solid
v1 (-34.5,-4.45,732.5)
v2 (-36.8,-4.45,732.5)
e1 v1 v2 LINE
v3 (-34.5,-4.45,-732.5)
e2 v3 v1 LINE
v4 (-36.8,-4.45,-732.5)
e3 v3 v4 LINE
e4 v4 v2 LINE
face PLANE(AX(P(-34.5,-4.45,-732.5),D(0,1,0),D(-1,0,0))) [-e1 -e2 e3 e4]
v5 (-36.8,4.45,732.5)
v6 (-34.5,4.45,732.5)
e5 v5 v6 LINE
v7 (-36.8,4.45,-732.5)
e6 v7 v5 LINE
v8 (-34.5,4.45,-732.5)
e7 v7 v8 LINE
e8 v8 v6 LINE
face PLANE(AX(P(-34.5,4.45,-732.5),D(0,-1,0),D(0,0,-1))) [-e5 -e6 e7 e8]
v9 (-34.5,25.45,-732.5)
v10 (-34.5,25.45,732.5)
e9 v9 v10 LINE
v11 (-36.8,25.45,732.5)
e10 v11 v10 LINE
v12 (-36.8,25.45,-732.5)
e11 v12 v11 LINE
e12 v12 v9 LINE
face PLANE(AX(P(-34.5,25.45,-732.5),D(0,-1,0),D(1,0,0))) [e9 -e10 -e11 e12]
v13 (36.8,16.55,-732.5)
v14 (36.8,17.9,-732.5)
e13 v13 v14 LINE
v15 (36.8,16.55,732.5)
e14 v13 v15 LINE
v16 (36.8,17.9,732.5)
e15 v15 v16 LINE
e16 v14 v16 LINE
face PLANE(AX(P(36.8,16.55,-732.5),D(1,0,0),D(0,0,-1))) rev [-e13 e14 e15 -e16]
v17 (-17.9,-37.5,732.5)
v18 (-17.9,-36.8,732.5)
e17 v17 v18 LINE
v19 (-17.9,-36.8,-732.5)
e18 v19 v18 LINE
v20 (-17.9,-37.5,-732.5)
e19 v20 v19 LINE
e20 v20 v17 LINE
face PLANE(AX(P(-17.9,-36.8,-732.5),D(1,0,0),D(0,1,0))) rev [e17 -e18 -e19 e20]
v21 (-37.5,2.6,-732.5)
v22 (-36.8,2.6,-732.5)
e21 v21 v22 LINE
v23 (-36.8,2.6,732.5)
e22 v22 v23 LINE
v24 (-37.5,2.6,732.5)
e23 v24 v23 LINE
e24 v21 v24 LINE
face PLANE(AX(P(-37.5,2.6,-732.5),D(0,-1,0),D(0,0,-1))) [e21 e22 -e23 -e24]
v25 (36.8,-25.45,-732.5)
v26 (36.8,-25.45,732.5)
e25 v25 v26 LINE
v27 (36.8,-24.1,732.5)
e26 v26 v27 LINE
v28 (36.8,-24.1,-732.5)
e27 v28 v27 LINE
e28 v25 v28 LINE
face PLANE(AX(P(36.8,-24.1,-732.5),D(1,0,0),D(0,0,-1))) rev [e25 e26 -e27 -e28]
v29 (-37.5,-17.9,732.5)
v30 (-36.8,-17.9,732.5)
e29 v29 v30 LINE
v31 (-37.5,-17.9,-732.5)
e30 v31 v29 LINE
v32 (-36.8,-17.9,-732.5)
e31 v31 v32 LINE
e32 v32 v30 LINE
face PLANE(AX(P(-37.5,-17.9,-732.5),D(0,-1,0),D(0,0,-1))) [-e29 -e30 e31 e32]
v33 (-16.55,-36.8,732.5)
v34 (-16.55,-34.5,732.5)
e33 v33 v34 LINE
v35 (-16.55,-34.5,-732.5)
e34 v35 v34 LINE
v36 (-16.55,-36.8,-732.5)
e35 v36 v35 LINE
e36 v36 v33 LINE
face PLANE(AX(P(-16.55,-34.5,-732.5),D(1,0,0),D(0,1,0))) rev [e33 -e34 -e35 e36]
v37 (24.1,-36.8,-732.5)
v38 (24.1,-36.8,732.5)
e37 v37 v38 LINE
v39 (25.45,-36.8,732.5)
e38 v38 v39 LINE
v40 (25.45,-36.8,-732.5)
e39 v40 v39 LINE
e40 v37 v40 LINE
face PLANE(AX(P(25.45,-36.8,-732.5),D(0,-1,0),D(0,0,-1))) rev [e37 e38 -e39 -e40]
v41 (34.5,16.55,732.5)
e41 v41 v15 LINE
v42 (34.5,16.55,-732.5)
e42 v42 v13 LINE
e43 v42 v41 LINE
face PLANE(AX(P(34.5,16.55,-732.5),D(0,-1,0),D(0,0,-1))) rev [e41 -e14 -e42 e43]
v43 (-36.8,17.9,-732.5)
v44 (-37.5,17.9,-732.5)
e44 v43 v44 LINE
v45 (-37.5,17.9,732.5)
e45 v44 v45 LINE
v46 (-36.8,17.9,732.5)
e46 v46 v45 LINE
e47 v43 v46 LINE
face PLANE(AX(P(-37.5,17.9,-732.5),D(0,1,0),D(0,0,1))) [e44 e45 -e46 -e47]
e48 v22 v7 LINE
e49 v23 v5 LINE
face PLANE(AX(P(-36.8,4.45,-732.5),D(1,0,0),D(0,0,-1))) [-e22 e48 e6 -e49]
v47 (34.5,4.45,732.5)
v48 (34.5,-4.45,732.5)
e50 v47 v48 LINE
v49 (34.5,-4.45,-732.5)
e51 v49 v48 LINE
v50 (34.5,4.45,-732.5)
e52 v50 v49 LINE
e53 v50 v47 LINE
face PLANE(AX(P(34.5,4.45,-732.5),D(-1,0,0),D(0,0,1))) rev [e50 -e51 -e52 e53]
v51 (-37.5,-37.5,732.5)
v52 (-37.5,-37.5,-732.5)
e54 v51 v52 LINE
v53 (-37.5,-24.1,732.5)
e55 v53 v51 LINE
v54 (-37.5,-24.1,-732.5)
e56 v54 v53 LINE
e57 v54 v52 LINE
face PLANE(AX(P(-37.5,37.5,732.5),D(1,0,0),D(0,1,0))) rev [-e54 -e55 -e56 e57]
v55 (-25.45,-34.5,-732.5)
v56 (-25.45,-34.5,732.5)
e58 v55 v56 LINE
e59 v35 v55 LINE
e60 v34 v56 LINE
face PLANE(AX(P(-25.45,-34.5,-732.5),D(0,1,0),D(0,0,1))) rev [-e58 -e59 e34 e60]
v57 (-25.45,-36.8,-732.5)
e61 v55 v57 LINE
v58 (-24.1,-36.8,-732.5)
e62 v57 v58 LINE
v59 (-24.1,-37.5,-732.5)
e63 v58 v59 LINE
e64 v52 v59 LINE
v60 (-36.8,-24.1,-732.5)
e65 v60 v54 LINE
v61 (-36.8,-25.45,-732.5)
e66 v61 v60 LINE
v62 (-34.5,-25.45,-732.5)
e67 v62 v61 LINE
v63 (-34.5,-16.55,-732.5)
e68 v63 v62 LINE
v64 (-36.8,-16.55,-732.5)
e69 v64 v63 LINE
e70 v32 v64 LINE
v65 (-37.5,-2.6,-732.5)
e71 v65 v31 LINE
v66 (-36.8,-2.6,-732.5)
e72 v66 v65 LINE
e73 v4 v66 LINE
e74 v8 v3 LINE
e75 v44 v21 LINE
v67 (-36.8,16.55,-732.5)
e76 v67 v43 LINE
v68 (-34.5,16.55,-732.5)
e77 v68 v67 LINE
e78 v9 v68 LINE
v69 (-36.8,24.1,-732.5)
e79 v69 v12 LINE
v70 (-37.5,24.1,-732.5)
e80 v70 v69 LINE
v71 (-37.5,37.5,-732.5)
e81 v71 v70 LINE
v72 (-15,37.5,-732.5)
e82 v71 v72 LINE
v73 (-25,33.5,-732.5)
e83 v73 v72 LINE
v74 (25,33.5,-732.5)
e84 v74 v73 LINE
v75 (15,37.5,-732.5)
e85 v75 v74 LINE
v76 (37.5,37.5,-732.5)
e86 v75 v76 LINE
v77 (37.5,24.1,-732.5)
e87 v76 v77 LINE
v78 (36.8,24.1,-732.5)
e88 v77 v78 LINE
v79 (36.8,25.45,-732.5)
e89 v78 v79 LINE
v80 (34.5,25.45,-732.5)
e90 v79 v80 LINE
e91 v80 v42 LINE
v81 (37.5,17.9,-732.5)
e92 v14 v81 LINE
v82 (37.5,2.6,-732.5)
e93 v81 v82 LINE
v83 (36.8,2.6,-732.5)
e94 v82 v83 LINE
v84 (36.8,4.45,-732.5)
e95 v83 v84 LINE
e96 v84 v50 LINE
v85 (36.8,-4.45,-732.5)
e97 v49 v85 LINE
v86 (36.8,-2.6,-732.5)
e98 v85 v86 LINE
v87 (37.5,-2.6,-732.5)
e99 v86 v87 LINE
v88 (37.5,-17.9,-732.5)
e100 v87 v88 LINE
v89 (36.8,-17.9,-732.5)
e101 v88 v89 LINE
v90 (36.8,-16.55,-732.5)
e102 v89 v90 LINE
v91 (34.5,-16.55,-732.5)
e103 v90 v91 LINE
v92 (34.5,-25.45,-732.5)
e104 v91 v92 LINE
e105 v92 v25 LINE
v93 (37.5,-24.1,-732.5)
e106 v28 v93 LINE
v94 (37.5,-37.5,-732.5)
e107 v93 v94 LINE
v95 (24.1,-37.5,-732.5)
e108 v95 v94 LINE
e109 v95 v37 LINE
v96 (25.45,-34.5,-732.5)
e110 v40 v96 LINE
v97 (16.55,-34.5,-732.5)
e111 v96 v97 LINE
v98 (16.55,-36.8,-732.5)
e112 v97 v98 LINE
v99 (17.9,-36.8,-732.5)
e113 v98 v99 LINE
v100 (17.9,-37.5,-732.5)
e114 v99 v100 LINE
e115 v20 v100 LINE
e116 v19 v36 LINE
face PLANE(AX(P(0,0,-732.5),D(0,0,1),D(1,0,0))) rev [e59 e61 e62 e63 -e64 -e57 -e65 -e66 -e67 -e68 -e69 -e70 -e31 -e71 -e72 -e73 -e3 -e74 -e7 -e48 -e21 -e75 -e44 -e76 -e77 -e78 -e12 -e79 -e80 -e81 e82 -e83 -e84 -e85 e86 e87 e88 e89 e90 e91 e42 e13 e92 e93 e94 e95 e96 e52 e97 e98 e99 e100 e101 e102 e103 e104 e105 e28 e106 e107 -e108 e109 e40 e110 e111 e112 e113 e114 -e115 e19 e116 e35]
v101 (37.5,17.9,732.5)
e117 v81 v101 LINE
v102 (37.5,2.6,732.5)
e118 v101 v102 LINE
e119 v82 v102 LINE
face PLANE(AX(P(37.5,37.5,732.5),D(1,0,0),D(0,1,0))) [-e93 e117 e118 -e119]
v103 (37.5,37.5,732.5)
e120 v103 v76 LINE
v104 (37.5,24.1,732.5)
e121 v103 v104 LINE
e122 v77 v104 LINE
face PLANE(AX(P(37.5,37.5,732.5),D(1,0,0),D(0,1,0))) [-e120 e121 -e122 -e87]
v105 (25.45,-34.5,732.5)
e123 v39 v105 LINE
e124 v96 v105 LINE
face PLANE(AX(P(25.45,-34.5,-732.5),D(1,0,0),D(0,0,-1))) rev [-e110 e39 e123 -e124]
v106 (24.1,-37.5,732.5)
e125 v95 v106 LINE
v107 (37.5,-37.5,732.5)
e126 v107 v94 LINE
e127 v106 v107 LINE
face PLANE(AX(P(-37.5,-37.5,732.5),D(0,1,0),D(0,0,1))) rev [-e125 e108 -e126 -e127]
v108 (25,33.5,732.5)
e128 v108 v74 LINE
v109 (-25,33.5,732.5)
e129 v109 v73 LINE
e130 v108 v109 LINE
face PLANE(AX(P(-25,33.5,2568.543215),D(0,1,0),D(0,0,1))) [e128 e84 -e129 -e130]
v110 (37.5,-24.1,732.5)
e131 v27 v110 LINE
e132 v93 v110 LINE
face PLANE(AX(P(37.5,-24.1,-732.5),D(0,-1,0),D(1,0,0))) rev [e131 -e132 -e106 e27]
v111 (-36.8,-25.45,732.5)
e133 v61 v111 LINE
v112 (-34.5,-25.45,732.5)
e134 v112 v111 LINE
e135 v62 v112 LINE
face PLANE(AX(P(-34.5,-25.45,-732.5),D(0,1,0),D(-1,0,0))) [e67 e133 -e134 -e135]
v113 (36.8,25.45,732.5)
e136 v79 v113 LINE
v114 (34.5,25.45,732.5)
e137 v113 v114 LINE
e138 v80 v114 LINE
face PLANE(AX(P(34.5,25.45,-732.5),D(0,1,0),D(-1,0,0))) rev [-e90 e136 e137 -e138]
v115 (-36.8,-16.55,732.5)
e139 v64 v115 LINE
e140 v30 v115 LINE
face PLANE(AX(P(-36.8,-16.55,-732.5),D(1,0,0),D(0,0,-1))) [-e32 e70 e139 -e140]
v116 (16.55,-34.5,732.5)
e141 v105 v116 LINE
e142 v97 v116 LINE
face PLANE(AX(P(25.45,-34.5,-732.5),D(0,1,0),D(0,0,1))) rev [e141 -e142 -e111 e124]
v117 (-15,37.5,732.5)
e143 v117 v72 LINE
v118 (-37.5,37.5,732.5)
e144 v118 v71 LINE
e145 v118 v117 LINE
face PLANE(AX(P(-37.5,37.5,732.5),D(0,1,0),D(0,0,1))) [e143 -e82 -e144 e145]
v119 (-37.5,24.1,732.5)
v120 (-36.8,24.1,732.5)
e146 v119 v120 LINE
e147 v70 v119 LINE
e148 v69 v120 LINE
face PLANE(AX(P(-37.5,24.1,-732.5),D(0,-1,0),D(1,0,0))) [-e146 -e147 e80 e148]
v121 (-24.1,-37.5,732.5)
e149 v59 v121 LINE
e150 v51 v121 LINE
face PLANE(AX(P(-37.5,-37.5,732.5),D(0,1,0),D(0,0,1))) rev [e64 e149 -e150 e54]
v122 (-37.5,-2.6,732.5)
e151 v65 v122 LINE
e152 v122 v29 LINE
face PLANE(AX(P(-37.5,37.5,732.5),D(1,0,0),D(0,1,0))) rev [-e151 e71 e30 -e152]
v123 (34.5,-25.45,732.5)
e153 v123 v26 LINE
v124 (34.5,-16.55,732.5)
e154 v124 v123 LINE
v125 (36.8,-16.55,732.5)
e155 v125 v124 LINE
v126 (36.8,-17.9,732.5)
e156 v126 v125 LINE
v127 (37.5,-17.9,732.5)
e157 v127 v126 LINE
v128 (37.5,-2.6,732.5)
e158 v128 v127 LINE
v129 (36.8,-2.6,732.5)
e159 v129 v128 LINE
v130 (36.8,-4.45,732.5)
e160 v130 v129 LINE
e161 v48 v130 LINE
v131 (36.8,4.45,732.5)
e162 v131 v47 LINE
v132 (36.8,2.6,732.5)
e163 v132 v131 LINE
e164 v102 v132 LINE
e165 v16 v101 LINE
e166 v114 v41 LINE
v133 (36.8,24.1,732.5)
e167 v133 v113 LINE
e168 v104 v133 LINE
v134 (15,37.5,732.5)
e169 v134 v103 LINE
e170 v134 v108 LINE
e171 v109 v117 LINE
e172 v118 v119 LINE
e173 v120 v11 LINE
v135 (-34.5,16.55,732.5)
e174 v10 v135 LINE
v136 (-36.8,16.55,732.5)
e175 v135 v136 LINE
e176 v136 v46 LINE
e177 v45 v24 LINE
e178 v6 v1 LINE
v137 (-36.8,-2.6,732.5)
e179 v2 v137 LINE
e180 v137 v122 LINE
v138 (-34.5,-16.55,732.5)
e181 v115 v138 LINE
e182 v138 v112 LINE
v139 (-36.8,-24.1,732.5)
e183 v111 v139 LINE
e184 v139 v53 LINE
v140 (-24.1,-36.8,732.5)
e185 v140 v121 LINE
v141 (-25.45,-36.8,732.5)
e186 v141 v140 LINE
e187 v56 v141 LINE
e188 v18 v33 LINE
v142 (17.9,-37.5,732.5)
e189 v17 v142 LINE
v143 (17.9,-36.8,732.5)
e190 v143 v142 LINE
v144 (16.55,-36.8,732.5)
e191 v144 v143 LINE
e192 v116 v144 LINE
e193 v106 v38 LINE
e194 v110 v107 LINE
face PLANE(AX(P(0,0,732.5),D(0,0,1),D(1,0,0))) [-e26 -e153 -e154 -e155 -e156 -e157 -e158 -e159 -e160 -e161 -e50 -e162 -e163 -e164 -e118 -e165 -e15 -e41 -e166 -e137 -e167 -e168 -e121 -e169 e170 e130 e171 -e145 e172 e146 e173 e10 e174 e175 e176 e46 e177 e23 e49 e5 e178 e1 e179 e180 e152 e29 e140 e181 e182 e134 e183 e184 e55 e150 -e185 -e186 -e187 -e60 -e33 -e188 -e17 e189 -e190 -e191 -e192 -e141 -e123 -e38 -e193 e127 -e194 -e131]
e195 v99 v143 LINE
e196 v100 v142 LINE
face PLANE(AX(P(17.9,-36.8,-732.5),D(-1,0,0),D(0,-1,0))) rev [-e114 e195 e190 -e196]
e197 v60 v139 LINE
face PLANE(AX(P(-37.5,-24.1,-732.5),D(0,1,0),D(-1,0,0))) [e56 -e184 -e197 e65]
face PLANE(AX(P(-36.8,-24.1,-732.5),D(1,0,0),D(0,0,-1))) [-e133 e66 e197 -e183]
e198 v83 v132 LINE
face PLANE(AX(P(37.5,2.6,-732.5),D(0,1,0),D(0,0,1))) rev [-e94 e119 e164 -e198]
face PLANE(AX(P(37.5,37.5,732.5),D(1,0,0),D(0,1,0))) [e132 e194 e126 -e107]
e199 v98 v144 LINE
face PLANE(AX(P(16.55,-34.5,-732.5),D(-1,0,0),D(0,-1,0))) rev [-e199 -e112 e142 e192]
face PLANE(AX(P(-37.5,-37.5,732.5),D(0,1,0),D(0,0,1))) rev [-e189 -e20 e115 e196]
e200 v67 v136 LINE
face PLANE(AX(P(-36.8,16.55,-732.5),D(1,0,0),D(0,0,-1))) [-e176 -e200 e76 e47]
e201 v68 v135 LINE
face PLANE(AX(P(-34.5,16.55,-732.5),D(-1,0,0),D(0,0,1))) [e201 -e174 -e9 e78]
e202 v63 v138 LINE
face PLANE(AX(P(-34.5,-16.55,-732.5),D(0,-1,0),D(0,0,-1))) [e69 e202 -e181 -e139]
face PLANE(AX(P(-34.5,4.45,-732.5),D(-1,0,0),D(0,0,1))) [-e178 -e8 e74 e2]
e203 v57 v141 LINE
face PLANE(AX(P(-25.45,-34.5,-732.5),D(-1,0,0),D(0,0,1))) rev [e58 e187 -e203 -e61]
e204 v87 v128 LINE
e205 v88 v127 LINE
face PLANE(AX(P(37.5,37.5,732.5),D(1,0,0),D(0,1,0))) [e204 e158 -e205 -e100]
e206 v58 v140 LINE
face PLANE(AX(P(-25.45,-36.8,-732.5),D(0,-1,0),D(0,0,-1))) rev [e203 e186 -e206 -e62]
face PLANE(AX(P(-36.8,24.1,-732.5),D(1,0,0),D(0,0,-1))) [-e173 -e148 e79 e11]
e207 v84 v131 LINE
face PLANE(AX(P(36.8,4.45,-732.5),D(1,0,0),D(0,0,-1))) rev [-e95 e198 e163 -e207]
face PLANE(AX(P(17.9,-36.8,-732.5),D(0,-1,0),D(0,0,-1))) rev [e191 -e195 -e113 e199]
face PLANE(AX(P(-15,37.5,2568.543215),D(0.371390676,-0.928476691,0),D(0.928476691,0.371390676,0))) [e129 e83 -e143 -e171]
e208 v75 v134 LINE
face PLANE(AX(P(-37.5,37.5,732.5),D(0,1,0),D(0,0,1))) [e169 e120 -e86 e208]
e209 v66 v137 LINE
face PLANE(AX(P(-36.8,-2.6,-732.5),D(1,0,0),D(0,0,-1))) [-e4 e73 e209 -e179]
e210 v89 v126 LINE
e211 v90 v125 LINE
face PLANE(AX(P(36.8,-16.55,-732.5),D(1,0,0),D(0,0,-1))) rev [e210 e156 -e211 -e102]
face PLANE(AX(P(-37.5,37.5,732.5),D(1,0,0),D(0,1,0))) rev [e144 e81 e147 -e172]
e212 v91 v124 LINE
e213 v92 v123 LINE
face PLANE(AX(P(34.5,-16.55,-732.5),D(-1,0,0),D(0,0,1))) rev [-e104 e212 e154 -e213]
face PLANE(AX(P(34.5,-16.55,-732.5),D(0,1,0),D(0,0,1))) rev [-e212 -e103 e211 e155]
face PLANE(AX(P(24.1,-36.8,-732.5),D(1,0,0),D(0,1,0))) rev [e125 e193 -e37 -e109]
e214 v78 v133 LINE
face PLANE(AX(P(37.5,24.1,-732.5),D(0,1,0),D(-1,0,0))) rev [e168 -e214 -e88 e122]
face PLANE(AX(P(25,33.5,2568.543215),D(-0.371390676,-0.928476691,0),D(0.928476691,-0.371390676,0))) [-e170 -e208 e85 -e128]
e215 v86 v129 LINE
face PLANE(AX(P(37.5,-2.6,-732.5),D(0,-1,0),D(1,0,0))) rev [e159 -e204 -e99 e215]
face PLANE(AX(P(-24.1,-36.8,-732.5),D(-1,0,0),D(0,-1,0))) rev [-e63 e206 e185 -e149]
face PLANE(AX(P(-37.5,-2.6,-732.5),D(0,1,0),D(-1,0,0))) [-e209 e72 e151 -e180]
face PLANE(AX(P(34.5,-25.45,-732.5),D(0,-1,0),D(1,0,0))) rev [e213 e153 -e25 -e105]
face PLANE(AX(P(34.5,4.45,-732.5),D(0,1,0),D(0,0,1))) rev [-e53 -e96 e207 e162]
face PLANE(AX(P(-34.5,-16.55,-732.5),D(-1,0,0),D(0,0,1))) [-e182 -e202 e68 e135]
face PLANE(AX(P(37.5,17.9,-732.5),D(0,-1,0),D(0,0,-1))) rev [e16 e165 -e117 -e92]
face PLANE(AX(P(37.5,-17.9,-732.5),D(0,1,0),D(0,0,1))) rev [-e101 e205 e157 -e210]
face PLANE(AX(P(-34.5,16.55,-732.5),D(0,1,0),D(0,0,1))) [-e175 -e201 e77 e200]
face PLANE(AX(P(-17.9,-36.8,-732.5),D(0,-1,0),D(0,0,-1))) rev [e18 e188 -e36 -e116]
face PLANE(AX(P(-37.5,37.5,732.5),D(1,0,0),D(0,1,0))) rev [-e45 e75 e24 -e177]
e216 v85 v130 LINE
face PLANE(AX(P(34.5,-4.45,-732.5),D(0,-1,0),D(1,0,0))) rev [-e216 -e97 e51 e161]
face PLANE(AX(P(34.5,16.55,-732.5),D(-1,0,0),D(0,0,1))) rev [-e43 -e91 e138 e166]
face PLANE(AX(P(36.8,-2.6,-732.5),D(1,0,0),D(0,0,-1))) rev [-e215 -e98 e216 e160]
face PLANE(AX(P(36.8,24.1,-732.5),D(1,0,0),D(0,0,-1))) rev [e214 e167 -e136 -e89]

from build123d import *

# Parameters (mm, degrees)
SKETCH_1_W               = 75
SKETCH_1_H               = 75
EXTRUDE_1_DEPTH          = 732.5
CUT_EXTRUDE_1_DEPTH      = 732.5
CUT_EXTRUDE_2_DEPTH      = 1465
CUT_EXTRUDE_3_DEPTH      = 1466.959583345
CUT_EXTRUDE_3_DEPTH_BACK = 1466.959583345


with BuildPart() as part:
    # 草图1 → 凸台-拉伸1 (new, symmetric)
    with BuildSketch(Plane.XY):
        Rectangle(SKETCH_1_W, SKETCH_1_H)
    extrude(amount=EXTRUDE_1_DEPTH, both=True)

    # 草图2 → 切除-拉伸1 (cut, symmetric)
    with BuildSketch(Plane.XY):
        Polygon((-17.9, -36.8), (-16.55, -36.8), (-16.55, -34.5), (-25.45, -34.5), (-25.45, -36.8), (-24.1, -36.8), (-24.1, -37.5), (-17.9, -37.5), align=None)
        Polygon((16.55, -34.5), (16.55, -36.8), (17.9, -36.8), (17.9, -37.5), (24.1, -37.5), (24.1, -36.8), (25.45, -36.8), (25.45, -34.5), align=None)
    extrude(amount=CUT_EXTRUDE_1_DEPTH, both=True, mode=Mode.SUBTRACT)

    # 草图3 → 切除-拉伸2 (cut)
    with BuildSketch(Plane.XY.offset(732.5)):
        Polygon((37.5, 2.6), (36.8, 2.6), (36.8, 4.45), (34.5, 4.45), (34.5, -4.45), (36.8, -4.45), (36.8, -2.6), (37.5, -2.6), align=None)
        Polygon((37.5, -17.9), (36.8, -17.9), (36.8, -16.55), (34.5, -16.55), (34.5, -25.45), (36.8, -25.45), (36.8, -24.1), (37.5, -24.1), align=None)
        Polygon((36.8, 24.1), (36.8, 25.45), (34.5, 25.45), (34.5, 16.55), (36.8, 16.55), (36.8, 17.9), (37.5, 17.9), (37.5, 24.1), align=None)
    cut_extrude_2 = extrude(amount=-CUT_EXTRUDE_2_DEPTH, mode=Mode.SUBTRACT)

    # 镜向1: 切除-拉伸2 across plane
    add(cut_extrude_2.mirror(Plane(origin=(0, 0, 0), x_dir=(0, 0, 1), z_dir=(1, 0, 0))), mode=Mode.SUBTRACT)

    # 草图4 → 切除-拉伸3 (cut, two sides: drawn at the far end of the back side and taken through both)
    with BuildSketch(Plane.XY.offset(732.5).offset(-CUT_EXTRUDE_3_DEPTH_BACK)):
        Polygon((164.287302387, 109.214920955), (-15, 37.5), (-25, 33.5), (25, 33.5), (15, 37.5), (-164.287302387, 109.214920955), (-164.287302387, -276.981747517), (164.287302387, -276.981747517), align=None)
    extrude(amount=CUT_EXTRUDE_3_DEPTH + CUT_EXTRUDE_3_DEPTH_BACK, mode=Mode.SUBTRACT)


solid = part.part
